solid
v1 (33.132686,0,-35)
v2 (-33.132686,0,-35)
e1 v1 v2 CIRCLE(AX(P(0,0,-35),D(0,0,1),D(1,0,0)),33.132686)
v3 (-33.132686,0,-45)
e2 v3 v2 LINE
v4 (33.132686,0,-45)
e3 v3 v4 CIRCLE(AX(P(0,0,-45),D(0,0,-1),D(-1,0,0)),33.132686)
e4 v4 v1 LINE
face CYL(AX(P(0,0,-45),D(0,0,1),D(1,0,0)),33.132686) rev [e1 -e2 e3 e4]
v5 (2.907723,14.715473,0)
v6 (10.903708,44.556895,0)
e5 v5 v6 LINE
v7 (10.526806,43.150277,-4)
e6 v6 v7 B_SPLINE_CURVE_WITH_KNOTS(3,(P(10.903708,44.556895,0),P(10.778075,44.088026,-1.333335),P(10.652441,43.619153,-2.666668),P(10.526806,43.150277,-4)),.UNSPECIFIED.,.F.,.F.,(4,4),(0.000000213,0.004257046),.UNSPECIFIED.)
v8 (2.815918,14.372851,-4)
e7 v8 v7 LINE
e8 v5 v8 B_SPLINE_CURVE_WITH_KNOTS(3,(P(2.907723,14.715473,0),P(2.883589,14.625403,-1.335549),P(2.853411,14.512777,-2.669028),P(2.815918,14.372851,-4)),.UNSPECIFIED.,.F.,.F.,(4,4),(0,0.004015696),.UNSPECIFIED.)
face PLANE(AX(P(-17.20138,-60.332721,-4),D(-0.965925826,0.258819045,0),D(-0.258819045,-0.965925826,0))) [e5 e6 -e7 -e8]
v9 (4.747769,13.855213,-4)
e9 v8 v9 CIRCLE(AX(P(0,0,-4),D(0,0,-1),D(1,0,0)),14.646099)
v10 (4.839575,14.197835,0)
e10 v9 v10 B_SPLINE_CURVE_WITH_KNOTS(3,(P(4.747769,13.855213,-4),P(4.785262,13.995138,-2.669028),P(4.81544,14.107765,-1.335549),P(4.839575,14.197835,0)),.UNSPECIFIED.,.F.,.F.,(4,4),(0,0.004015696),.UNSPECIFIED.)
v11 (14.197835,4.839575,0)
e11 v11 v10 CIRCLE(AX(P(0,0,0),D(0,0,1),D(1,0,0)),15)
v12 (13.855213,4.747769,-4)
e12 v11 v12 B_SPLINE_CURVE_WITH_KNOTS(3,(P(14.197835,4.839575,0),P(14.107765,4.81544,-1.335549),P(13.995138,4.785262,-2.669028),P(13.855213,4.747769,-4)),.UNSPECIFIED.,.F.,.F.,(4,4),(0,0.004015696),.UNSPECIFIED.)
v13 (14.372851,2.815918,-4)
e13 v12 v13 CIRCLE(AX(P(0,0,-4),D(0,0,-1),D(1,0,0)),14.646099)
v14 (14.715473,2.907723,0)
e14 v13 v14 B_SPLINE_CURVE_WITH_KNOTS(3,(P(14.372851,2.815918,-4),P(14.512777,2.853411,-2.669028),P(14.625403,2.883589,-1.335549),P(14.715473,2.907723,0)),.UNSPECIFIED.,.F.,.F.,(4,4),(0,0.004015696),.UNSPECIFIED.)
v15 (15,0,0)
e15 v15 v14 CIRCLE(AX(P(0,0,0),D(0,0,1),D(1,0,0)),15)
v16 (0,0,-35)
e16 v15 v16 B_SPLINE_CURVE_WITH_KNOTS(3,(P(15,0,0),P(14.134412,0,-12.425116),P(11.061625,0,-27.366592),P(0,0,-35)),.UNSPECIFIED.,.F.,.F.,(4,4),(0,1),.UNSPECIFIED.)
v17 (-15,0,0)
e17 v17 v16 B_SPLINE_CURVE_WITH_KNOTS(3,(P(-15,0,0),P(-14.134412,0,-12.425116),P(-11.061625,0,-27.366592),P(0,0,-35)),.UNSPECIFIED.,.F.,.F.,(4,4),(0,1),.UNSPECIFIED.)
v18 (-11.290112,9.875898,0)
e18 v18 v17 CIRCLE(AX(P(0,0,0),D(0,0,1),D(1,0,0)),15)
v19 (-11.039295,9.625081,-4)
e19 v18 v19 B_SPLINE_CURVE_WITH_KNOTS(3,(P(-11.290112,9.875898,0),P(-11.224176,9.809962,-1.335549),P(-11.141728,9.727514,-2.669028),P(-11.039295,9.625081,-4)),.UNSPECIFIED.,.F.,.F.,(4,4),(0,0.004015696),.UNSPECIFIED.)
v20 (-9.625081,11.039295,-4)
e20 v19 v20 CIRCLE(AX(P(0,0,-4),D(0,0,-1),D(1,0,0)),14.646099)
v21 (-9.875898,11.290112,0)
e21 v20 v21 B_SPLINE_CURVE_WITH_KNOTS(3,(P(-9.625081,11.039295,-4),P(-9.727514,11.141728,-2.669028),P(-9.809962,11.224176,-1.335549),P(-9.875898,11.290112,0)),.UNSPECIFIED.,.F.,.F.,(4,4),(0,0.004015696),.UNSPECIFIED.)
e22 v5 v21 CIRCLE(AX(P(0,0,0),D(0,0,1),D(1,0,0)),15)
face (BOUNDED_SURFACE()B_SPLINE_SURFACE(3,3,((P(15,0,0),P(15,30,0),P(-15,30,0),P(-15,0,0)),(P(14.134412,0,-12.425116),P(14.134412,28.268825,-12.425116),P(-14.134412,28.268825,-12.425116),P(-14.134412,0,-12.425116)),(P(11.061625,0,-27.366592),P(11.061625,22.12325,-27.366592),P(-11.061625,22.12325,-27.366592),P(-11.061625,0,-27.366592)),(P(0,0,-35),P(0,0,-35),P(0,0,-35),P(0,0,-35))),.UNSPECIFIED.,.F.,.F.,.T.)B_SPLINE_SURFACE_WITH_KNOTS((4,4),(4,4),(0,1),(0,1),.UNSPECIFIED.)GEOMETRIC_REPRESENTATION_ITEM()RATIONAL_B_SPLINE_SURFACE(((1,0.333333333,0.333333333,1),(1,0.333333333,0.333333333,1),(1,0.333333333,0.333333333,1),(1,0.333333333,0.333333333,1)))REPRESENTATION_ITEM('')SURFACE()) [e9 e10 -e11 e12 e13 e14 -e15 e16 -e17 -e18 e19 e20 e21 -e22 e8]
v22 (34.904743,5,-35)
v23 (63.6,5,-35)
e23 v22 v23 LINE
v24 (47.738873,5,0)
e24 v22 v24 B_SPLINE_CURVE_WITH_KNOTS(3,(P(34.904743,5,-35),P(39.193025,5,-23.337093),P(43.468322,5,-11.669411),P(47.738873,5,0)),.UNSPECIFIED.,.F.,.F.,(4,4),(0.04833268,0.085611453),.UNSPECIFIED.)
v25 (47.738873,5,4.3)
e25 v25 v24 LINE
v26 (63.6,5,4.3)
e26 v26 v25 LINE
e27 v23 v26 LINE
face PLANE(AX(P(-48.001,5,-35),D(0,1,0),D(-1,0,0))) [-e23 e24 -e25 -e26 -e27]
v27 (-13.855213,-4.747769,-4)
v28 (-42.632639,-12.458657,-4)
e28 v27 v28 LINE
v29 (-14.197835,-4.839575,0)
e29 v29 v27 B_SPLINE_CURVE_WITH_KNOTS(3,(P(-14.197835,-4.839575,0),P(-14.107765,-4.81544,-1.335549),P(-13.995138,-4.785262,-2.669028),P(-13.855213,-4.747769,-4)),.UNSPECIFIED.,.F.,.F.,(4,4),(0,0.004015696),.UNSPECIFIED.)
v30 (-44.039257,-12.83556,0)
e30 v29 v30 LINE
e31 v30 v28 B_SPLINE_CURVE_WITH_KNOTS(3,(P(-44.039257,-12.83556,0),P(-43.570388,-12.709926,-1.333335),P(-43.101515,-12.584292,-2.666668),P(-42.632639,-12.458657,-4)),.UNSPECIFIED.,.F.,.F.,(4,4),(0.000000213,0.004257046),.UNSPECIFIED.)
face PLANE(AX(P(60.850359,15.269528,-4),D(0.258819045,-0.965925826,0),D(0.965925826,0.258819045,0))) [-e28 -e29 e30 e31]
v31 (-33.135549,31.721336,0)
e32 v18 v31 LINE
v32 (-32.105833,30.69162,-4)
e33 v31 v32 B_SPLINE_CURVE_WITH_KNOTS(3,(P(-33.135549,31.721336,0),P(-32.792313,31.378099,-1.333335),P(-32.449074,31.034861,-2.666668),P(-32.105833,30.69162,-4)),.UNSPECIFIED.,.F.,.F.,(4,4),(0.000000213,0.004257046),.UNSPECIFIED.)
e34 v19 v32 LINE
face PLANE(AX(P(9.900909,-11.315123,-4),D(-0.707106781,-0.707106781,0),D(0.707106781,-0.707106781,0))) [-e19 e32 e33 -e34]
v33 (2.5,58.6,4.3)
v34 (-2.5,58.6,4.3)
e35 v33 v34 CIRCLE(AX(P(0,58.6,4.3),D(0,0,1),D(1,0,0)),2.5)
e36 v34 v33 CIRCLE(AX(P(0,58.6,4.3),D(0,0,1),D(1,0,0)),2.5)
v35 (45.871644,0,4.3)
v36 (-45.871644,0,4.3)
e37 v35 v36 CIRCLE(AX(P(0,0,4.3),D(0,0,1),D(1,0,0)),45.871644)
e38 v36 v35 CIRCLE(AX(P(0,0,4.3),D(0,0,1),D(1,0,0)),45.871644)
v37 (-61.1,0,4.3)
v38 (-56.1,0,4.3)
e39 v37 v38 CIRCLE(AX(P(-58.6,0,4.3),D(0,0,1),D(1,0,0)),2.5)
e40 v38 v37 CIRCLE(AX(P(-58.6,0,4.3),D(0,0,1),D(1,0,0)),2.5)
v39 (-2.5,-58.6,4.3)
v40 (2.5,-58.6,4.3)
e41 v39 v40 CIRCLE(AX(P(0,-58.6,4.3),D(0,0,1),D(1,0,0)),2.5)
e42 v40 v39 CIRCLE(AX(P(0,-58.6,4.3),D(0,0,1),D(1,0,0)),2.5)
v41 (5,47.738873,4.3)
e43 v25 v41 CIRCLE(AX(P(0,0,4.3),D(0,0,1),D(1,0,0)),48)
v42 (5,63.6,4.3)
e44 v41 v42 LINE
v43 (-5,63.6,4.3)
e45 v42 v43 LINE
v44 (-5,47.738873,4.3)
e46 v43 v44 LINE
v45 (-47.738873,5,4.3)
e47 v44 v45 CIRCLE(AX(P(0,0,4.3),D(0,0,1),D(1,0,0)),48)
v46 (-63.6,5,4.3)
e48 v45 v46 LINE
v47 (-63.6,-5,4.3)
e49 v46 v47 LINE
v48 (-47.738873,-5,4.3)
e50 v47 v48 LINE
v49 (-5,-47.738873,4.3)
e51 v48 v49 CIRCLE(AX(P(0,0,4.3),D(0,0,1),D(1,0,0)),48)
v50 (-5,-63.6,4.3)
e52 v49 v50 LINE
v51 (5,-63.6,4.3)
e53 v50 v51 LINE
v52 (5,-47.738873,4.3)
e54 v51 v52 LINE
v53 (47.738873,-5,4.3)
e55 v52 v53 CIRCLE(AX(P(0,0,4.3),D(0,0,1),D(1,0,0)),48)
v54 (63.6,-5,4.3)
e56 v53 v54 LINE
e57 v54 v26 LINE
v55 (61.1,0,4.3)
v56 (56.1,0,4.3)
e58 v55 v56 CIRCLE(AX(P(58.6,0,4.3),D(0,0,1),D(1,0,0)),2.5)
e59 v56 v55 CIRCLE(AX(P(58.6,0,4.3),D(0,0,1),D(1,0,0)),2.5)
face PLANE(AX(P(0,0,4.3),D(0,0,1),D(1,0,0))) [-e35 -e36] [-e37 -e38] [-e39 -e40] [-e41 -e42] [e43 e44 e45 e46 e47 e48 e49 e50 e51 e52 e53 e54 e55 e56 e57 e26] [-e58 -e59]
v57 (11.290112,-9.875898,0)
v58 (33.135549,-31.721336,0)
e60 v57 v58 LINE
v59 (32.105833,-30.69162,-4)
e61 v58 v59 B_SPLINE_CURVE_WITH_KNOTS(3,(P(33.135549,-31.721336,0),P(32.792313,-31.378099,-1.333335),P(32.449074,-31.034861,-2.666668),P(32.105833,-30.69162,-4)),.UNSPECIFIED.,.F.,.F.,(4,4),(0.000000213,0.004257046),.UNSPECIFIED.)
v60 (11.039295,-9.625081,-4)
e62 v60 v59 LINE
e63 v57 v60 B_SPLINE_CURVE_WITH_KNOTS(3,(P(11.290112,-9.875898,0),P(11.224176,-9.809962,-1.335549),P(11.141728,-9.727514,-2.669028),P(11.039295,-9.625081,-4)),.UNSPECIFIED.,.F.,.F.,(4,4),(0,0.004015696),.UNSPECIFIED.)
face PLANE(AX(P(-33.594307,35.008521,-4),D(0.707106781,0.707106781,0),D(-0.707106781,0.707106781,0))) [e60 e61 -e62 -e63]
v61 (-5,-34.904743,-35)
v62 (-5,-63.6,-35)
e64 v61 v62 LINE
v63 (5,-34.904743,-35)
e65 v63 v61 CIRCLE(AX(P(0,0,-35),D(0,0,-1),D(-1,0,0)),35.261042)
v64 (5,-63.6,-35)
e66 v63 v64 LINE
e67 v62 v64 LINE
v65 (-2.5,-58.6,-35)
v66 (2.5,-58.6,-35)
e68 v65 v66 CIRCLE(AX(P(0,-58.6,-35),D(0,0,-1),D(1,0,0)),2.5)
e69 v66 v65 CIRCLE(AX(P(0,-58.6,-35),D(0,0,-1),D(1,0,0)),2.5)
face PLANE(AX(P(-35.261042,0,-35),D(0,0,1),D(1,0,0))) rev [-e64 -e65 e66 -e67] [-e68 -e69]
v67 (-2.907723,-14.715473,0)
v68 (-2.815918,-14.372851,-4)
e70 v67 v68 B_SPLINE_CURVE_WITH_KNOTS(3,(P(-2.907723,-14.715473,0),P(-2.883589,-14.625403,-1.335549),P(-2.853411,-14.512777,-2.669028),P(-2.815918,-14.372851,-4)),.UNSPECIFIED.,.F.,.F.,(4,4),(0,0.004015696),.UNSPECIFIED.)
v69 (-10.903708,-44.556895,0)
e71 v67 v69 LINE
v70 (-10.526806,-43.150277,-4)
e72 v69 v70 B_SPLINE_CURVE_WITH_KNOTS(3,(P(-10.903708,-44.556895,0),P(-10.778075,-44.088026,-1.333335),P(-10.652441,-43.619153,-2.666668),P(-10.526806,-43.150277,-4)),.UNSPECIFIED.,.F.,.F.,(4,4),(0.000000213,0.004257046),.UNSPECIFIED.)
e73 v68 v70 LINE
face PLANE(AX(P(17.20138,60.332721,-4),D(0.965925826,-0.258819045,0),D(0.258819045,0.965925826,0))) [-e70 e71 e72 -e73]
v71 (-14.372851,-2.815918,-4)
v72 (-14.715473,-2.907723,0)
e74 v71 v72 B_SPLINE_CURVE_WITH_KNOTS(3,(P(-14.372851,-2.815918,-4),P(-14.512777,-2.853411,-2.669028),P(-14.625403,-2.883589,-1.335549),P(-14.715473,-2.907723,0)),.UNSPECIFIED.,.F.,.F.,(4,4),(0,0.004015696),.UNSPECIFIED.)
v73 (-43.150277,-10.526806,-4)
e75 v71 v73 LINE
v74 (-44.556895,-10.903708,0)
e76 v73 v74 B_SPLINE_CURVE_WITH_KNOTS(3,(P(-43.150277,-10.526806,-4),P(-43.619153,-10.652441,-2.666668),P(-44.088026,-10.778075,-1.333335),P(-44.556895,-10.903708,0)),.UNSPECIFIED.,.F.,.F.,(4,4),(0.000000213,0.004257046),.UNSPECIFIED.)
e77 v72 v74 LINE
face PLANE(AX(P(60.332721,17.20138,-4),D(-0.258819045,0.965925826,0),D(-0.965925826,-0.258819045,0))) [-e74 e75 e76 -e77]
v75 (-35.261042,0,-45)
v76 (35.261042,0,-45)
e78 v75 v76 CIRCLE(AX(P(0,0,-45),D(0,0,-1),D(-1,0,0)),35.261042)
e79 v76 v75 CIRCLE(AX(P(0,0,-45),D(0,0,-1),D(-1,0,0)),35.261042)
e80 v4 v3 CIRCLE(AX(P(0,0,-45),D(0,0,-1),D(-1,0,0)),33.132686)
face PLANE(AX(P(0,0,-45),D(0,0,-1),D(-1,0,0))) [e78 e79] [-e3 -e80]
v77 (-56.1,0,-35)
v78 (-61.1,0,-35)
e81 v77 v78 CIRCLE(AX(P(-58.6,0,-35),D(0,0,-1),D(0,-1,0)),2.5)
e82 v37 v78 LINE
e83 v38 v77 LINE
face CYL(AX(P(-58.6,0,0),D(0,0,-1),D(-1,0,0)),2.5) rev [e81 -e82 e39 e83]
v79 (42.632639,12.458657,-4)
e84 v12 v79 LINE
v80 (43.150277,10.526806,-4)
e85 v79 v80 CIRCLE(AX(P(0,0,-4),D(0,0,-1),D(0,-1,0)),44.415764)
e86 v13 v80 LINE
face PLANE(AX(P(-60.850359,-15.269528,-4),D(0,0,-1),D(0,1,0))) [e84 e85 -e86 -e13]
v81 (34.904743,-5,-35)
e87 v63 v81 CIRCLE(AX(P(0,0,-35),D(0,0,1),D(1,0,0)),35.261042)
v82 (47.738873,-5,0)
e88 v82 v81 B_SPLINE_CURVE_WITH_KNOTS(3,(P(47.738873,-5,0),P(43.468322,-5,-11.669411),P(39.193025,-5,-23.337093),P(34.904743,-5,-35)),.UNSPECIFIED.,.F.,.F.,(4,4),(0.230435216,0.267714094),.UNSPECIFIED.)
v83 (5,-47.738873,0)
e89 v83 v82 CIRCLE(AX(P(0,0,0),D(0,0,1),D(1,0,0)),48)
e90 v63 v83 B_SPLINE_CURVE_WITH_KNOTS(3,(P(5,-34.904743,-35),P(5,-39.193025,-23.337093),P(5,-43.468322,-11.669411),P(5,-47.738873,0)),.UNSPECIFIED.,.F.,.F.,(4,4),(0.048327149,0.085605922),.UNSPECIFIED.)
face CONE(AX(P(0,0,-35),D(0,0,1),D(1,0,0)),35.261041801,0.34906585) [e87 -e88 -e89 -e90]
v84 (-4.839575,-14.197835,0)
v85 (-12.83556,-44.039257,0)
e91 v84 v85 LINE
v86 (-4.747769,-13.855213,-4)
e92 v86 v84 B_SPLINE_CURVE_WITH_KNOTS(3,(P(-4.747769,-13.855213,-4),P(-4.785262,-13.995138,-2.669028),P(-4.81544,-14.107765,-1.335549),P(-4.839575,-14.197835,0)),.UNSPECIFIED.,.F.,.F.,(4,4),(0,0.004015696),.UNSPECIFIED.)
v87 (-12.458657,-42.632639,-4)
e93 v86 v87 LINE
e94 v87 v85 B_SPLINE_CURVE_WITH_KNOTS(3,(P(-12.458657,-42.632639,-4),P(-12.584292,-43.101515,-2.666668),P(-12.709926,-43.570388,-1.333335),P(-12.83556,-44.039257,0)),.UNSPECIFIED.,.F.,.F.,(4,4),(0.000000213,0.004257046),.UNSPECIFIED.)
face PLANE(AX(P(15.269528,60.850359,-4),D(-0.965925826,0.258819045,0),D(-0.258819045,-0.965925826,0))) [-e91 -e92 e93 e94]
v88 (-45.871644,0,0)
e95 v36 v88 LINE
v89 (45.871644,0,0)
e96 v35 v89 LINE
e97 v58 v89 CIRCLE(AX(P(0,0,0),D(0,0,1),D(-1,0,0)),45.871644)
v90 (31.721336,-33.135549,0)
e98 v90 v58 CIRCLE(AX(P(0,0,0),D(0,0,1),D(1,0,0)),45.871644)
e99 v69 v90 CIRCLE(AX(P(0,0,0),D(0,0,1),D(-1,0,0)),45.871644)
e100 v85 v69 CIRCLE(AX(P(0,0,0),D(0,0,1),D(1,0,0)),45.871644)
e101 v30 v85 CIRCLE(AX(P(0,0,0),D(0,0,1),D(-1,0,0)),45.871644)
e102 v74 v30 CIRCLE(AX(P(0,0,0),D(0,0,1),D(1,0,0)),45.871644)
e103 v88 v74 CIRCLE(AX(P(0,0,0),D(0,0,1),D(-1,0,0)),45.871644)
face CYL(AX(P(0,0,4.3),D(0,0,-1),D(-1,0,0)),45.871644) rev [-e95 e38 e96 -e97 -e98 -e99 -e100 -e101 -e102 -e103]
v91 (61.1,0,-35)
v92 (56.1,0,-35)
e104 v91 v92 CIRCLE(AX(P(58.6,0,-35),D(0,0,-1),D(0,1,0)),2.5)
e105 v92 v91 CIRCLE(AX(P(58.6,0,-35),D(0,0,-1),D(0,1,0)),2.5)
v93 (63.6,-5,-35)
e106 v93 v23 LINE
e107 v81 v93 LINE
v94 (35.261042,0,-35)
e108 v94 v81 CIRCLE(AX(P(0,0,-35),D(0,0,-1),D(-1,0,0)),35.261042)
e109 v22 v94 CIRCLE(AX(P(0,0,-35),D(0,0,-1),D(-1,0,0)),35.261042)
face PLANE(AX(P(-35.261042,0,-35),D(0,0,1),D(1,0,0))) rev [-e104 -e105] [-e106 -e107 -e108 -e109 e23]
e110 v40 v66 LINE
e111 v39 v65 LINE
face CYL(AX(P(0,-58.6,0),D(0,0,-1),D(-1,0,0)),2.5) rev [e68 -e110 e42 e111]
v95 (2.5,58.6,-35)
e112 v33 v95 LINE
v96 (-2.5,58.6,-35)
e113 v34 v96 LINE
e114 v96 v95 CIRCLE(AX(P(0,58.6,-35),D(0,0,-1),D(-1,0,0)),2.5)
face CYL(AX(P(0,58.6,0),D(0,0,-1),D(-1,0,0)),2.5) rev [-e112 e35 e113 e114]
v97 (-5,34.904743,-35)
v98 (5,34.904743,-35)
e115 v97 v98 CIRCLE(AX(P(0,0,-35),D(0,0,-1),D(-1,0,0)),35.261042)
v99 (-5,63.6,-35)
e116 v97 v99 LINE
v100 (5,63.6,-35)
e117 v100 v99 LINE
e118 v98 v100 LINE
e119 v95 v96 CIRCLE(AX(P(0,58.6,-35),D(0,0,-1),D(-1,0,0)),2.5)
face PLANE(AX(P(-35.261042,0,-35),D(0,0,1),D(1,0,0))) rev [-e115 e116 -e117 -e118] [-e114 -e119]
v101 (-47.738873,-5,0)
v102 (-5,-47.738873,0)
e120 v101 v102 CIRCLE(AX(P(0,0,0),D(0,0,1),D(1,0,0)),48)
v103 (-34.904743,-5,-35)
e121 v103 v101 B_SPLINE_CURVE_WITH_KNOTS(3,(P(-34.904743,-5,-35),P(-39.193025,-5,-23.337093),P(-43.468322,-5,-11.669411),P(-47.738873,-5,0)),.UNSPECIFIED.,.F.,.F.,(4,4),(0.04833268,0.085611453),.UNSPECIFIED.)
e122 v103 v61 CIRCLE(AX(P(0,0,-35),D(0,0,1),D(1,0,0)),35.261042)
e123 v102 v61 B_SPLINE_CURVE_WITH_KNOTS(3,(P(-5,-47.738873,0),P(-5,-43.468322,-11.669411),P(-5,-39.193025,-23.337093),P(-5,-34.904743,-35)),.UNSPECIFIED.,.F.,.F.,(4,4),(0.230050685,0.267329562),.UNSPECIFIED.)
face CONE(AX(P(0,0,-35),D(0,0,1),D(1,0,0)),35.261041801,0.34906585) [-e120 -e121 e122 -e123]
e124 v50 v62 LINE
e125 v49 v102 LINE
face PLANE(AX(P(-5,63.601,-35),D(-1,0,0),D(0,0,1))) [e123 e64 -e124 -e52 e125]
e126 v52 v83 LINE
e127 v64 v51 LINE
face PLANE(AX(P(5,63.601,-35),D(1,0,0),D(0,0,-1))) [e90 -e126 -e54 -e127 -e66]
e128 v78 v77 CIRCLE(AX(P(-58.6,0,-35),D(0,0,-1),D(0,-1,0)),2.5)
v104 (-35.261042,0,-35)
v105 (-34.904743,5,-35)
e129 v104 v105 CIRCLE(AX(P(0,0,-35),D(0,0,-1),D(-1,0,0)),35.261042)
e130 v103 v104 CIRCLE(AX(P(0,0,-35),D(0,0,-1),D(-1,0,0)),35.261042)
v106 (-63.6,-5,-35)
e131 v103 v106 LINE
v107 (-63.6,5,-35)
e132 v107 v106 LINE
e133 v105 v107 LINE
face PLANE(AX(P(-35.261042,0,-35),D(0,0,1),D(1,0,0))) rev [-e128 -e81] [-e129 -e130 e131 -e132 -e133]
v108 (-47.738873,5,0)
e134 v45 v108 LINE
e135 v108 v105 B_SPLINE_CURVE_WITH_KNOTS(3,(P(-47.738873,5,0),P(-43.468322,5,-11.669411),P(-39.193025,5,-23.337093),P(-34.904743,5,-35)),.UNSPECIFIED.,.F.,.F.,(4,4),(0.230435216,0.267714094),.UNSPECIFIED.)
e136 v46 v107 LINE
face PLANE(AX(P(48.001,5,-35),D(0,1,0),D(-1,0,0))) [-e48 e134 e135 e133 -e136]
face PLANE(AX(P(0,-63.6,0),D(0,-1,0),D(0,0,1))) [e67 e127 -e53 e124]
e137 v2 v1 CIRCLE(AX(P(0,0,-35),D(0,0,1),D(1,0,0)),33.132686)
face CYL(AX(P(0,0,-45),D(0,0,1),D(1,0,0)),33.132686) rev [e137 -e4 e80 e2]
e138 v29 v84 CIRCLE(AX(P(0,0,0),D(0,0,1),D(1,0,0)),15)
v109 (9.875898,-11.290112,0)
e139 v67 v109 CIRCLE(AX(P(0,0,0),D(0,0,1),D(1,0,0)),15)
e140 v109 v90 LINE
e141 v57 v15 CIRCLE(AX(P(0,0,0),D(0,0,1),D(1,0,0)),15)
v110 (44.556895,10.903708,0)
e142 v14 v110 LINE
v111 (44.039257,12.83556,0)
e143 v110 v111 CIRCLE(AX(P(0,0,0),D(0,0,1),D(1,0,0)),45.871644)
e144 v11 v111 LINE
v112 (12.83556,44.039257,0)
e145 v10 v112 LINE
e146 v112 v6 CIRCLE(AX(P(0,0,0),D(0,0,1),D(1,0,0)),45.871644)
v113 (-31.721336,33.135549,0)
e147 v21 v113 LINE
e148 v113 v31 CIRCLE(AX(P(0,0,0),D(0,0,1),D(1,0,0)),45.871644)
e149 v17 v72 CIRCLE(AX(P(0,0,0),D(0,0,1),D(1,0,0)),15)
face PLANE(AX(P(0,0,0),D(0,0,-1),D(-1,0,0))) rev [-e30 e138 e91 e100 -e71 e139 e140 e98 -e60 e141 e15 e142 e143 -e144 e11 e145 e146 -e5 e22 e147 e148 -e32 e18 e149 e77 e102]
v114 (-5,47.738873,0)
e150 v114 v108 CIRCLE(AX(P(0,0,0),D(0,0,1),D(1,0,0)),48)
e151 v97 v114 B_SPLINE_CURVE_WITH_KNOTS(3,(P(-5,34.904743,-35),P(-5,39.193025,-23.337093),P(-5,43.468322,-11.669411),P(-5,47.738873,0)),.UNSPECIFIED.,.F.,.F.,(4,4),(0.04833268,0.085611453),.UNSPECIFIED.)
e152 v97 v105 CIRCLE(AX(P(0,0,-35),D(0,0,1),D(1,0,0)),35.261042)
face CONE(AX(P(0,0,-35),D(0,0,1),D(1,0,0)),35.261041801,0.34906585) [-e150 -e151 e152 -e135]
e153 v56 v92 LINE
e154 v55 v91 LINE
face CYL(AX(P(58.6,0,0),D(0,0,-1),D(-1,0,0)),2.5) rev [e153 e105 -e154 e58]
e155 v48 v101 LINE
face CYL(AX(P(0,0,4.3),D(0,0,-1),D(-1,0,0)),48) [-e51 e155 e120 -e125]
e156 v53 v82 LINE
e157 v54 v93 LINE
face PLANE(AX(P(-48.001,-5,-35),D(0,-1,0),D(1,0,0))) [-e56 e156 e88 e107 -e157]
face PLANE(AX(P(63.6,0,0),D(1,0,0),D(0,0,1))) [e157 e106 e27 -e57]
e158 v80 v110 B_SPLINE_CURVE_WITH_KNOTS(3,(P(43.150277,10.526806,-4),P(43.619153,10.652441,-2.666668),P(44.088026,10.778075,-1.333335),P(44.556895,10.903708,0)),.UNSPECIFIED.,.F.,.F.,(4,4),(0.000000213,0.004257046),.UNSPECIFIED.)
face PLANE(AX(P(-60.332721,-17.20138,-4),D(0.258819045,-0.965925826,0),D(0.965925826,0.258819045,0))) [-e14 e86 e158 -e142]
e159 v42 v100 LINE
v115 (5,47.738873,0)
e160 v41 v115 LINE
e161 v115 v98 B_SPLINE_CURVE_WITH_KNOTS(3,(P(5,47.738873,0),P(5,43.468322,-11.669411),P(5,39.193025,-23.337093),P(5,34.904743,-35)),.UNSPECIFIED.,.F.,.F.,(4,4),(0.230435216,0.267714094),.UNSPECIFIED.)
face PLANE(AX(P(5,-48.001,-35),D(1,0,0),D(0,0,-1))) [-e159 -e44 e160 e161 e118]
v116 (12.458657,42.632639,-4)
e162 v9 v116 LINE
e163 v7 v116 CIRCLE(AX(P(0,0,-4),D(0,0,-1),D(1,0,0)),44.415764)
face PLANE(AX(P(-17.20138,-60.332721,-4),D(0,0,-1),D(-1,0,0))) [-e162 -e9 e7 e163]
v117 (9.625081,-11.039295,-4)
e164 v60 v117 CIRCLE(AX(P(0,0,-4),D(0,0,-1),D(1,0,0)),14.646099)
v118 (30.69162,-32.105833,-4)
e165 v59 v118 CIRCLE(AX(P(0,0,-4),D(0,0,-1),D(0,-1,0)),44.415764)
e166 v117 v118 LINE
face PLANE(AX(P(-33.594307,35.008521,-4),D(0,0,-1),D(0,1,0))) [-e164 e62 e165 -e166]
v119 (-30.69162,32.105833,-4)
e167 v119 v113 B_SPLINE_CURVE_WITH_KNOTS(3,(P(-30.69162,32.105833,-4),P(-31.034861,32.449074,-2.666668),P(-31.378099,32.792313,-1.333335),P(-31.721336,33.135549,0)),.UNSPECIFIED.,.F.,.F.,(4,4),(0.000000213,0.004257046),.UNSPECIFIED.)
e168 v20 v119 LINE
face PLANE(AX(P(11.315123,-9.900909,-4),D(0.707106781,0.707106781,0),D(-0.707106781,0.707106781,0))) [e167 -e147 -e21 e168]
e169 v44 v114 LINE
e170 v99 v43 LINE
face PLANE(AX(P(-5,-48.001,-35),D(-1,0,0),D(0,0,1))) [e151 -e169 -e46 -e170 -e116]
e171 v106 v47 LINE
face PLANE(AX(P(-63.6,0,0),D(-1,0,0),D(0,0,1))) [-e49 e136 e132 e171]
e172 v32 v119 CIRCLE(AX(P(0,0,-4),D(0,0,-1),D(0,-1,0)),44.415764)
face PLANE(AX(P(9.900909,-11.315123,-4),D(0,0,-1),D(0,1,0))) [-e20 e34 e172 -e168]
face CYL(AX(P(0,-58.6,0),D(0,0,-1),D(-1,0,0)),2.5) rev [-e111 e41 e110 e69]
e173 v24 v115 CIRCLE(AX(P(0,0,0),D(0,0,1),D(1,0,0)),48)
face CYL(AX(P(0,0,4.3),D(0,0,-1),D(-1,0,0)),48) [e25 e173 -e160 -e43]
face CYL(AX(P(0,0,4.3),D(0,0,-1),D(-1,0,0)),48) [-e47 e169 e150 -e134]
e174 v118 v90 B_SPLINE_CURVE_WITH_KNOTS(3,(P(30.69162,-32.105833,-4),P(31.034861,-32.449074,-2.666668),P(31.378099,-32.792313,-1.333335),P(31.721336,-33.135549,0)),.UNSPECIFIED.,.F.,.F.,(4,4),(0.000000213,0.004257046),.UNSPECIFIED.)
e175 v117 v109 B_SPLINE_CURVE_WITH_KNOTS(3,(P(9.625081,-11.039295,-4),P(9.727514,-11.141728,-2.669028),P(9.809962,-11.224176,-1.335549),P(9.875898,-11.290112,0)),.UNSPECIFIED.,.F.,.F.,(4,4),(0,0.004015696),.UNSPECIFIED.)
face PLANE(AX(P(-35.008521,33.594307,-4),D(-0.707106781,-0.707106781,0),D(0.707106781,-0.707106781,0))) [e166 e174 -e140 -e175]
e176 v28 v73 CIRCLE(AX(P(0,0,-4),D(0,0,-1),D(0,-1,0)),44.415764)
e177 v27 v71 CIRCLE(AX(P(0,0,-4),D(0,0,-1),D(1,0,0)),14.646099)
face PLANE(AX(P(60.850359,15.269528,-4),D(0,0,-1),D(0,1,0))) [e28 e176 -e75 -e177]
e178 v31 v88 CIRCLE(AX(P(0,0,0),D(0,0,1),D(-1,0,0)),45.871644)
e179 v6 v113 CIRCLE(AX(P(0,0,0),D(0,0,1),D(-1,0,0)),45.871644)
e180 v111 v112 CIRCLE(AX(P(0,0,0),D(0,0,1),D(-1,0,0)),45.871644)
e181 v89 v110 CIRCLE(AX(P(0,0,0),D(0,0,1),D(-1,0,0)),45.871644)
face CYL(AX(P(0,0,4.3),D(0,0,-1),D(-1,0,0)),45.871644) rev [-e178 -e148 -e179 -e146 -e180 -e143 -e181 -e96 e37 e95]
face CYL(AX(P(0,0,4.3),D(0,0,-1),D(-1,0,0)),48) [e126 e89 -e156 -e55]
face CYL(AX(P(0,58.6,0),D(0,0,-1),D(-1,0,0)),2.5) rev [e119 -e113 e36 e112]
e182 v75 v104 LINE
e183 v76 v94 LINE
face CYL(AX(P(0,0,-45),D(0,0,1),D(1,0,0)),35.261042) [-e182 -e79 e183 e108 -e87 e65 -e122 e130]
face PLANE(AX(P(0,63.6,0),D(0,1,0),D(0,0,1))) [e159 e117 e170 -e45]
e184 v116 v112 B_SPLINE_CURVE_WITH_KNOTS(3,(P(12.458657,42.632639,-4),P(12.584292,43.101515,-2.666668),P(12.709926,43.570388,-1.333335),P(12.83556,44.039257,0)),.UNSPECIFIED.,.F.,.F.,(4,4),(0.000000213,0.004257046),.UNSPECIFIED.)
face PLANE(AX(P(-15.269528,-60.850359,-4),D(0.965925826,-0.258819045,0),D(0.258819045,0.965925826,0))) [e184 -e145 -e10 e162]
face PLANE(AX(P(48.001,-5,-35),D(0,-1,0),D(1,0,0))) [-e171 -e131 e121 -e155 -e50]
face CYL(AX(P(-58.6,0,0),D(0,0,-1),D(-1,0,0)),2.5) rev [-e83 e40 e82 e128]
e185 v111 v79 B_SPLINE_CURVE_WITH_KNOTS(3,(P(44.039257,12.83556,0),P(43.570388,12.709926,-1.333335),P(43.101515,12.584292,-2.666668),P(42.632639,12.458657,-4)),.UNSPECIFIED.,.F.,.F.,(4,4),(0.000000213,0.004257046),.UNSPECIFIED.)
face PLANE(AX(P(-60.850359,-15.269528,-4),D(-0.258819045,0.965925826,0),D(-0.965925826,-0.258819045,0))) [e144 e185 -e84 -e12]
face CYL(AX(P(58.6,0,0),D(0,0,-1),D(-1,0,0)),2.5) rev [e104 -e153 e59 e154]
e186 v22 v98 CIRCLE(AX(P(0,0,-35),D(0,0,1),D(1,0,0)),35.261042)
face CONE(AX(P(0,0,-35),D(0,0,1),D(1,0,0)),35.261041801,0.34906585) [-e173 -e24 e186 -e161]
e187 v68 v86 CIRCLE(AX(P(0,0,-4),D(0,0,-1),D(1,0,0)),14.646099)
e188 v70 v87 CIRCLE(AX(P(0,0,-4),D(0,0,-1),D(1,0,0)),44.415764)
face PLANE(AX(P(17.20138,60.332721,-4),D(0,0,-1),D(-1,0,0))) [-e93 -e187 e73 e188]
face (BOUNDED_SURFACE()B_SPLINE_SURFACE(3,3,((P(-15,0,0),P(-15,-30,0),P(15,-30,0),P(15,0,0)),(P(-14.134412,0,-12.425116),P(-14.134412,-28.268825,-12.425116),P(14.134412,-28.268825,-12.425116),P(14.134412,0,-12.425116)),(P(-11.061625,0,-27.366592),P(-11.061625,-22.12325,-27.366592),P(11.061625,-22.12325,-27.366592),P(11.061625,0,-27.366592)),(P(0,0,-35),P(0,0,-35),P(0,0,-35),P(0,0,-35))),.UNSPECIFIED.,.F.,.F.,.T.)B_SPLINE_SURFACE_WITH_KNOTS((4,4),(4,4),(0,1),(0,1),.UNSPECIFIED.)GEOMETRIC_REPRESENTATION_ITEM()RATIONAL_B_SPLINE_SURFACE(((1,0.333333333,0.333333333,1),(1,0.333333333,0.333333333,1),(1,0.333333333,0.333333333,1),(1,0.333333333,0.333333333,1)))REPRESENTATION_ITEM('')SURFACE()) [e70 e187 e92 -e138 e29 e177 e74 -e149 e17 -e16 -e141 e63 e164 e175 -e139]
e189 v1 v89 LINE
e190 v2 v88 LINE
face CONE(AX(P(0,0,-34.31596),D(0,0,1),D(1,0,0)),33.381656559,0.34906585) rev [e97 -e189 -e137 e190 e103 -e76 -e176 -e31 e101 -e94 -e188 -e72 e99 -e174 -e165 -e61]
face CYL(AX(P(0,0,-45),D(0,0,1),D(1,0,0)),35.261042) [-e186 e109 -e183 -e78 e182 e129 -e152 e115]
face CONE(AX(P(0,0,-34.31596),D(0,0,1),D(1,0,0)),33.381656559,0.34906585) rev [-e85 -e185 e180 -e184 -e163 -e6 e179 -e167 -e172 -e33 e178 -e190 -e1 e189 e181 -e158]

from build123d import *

# Parameters (mm, degrees)
SHELL2_T             = -2
BOSS_EXTRUDE10_REACH = 128.426
SKETCH20_W           = 10
SKETCH20_H           = 35
SKETCH21_R           = 2.5
CUT_EXTRUDE3_DEPTH   = 88.028501079
CIRPATTERN3_COUNT    = 4
SKETCH22_R           = 35.261041801
SKETCH22_R_2         = 33.132686256
BOSS_EXTRUDE11_DEPTH = 10
BOSS_EXTRUDE12_START = -5.388079
SKETCH24_W           = 4
SKETCH24_H           = 2
BOSS_EXTRUDE12_DEPTH = 31.259724
CIRPATTERN4_COUNT    = 6
SKETCH25_R           = 45.871644455
BOSS_EXTRUDE13_DEPTH = 4.3
SKETCH26_R           = 2.5
CUT_EXTRUDE4_DEPTH   = 103.569049913
SKETCH27_R           = 2.5
CUT_EXTRUDE5_DEPTH   = 103.569049913
SKETCH28_R           = 2.5
CUT_EXTRUDE6_DEPTH   = 103.569049913


with BuildPart() as part:
    # Sketch18 → Revolve1 (revolve)
    with BuildSketch(Plane(origin=(0, 0, 0), x_dir=(1, 0, 0), z_dir=(0, 1, 0)), mode=Mode.PRIVATE) as revolve1_sk:
        Polygon((0, 0), (-48, 0), (-35.261041801, 35), (0, 35), align=None)
    revolve(revolve1_sk.sketch.rotate(Axis((0, 0, 0), (0, 0, -1)), 180), axis=Axis((0, 0, 0), (0, 0, -1)))

    # Shell2
    shell2_openings = [part.faces().sort_by_distance(p)[0] for p in [
        (0, 0, -35),
        (0, 0, 0),
    ]]
    offset(amount=SHELL2_T, openings=shell2_openings, kind=Kind.INTERSECTION)

    # Sketch20 → Boss-Extrude10 (add, up to next)
    with BuildSketch(Plane(origin=(0, 63.6, 0), x_dir=(1, 0, 0), z_dir=(0, 1, 0)), mode=Mode.PRIVATE) as boss_extrude10_sk1:
        with Locations((0, 17.5)):
            Rectangle(SKETCH20_W, SKETCH20_H)
    boss_extrude10_tool1 = extrude(boss_extrude10_sk1.sketch, amount=-BOSS_EXTRUDE10_REACH, mode=Mode.PRIVATE) - part.part
    boss_extrude10 = boss_extrude10_tool1.solids().sort_by_distance((0, 63.6, -17.5))[0]
    add(boss_extrude10)

    # Sketch21 → Cut-Extrude3 (cut, through all)
    with BuildSketch(Plane(origin=(0, 0, -35), x_dir=(-1, 0, 0), z_dir=(0, 0, -1))):
        with Locations((0, 58.6)):
            Circle(SKETCH21_R)
    cut_extrude3 = extrude(amount=-CUT_EXTRUDE3_DEPTH, mode=Mode.SUBTRACT)

    # CirPattern3: Boss-Extrude10, Cut-Extrude3 ×4 about axis
    cirpattern3_axis = Axis((0, 0, 0), (0, 0, 1))
    add([boss_extrude10.rotate(cirpattern3_axis, i * 360 / CIRPATTERN3_COUNT) for i in range(1, CIRPATTERN3_COUNT)])
    add([cut_extrude3.rotate(cirpattern3_axis, i * 360 / CIRPATTERN3_COUNT) for i in range(1, CIRPATTERN3_COUNT)], mode=Mode.SUBTRACT)

    # Sketch22 → Boss-Extrude11 (add)
    with BuildSketch(Plane(origin=(0, 0, -35), x_dir=(-1, 0, 0), z_dir=(0, 0, -1))):
        with Locations(Location((0, 0, 0), (0, 0, 171.848007917))):
            Circle(SKETCH22_R)
        with Locations(Location((0, 0, 0), (0, 0, 180))):
            Circle(SKETCH22_R_2, mode=Mode.SUBTRACT)
    extrude(amount=BOSS_EXTRUDE11_DEPTH)



with BuildPart() as body_2:
    # Sketch23 → Revolve2 (revolve)
    with BuildSketch(Plane(origin=(0, 0, 0), x_dir=(1, 0, 0), z_dir=(0, 1, 0))):
        with BuildLine():
            Line((0, 0), (-15, 0))
            add(Edge.make_bspline(
                [(-15, 0), (-14.134412254, 12.425116283), (-11.061625239, 27.366592237), (0, 35)],
                knots=[0, 0, 0, 0, 1, 1, 1, 1], degree=3))
            Line((0, 35), (0, 0))
        make_face()
    revolve(axis=Axis((0, 0, 0), (0, 0, -1)))


with BuildPart() as part_1:
    add(part.part)

    add(body_2.part)  # Boss-Extrude12 merges body 2
    # Sketch24 → Boss-Extrude12 (add)
    with BuildSketch(Plane(origin=(-14.142135624, 14.142135624, 0), x_dir=(0, 0, -1), z_dir=(-0.7071067811865488, 0.7071067811865464, 0)).offset(BOSS_EXTRUDE12_START)):
        with Locations((2, 0)):
            Rectangle(SKETCH24_W, SKETCH24_H)
    boss_extrude12 = extrude(amount=BOSS_EXTRUDE12_DEPTH)

    # CirPattern4: Boss-Extrude12 ×6 about axis
    cirpattern4_axis = Axis((0, 0, 0), (0, 0, 1))
    for i in range(1, CIRPATTERN4_COUNT):
        add(boss_extrude12.rotate(cirpattern4_axis, i * 360 / CIRPATTERN4_COUNT))

    # Sketch25 → Boss-Extrude13 (add)
    with BuildSketch(Plane.XY):
        with BuildLine():
            Line((-47.738873049, 5), (-63.6, 5))
            Line((-63.6, 5), (-63.6, -5))
            Line((-63.6, -5), (-47.738873049, -5))
            ThreePointArc((-47.738873049, -5), (-33.941125497, -33.941125497), (-5, -47.738873049))
            Line((-5, -47.738873049), (-5, -63.6))
            Line((-5, -63.6), (5, -63.6))
            Line((5, -63.6), (5, -47.738873049))
            ThreePointArc((5, -47.738873049), (33.941125497, -33.941125497), (47.738873049, -5))
            Line((47.738873049, -5), (63.6, -5))
            Line((63.6, -5), (63.6, 5))
            Line((63.6, 5), (47.738873049, 5))
            ThreePointArc((47.738873049, 5), (33.941125497, 33.941125497), (5, 47.738873049))
            Line((5, 47.738873049), (5, 63.6))
            Line((5, 63.6), (-5, 63.6))
            Line((-5, 63.6), (-5, 47.738873049))
            ThreePointArc((-5, 47.738873049), (-33.941125497, 33.941125497), (-47.738873049, 5))
        make_face()
        Circle(SKETCH25_R, mode=Mode.SUBTRACT)
    extrude(amount=BOSS_EXTRUDE13_DEPTH)

    # Sketch26 → Cut-Extrude4 (cut, through all)
    with BuildSketch(Plane.XY.offset(4.3)):
        with Locations(Location((-58.6, 0, 0), (0, 0, 270))):
            Circle(SKETCH26_R)
    extrude(amount=-CUT_EXTRUDE4_DEPTH, mode=Mode.SUBTRACT)

    # Sketch27 → Cut-Extrude5 (cut, through all)
    with BuildSketch(Plane.XY.offset(4.3)):
        with Locations(Location((0, 58.6, 0), (0, 0, 180))):
            Circle(SKETCH27_R)
    extrude(amount=-CUT_EXTRUDE5_DEPTH, mode=Mode.SUBTRACT)

    # Sketch28 → Cut-Extrude6 (cut, through all)
    with BuildSketch(Plane.XY.offset(4.3)):
        with Locations((0, -58.6)):
            Circle(SKETCH28_R)
        with Locations(Location((58.6, 0, 0), (0, 0, 90))):
            Circle(SKETCH28_R)
    extrude(amount=-CUT_EXTRUDE6_DEPTH, mode=Mode.SUBTRACT)


solid = part_1.part
